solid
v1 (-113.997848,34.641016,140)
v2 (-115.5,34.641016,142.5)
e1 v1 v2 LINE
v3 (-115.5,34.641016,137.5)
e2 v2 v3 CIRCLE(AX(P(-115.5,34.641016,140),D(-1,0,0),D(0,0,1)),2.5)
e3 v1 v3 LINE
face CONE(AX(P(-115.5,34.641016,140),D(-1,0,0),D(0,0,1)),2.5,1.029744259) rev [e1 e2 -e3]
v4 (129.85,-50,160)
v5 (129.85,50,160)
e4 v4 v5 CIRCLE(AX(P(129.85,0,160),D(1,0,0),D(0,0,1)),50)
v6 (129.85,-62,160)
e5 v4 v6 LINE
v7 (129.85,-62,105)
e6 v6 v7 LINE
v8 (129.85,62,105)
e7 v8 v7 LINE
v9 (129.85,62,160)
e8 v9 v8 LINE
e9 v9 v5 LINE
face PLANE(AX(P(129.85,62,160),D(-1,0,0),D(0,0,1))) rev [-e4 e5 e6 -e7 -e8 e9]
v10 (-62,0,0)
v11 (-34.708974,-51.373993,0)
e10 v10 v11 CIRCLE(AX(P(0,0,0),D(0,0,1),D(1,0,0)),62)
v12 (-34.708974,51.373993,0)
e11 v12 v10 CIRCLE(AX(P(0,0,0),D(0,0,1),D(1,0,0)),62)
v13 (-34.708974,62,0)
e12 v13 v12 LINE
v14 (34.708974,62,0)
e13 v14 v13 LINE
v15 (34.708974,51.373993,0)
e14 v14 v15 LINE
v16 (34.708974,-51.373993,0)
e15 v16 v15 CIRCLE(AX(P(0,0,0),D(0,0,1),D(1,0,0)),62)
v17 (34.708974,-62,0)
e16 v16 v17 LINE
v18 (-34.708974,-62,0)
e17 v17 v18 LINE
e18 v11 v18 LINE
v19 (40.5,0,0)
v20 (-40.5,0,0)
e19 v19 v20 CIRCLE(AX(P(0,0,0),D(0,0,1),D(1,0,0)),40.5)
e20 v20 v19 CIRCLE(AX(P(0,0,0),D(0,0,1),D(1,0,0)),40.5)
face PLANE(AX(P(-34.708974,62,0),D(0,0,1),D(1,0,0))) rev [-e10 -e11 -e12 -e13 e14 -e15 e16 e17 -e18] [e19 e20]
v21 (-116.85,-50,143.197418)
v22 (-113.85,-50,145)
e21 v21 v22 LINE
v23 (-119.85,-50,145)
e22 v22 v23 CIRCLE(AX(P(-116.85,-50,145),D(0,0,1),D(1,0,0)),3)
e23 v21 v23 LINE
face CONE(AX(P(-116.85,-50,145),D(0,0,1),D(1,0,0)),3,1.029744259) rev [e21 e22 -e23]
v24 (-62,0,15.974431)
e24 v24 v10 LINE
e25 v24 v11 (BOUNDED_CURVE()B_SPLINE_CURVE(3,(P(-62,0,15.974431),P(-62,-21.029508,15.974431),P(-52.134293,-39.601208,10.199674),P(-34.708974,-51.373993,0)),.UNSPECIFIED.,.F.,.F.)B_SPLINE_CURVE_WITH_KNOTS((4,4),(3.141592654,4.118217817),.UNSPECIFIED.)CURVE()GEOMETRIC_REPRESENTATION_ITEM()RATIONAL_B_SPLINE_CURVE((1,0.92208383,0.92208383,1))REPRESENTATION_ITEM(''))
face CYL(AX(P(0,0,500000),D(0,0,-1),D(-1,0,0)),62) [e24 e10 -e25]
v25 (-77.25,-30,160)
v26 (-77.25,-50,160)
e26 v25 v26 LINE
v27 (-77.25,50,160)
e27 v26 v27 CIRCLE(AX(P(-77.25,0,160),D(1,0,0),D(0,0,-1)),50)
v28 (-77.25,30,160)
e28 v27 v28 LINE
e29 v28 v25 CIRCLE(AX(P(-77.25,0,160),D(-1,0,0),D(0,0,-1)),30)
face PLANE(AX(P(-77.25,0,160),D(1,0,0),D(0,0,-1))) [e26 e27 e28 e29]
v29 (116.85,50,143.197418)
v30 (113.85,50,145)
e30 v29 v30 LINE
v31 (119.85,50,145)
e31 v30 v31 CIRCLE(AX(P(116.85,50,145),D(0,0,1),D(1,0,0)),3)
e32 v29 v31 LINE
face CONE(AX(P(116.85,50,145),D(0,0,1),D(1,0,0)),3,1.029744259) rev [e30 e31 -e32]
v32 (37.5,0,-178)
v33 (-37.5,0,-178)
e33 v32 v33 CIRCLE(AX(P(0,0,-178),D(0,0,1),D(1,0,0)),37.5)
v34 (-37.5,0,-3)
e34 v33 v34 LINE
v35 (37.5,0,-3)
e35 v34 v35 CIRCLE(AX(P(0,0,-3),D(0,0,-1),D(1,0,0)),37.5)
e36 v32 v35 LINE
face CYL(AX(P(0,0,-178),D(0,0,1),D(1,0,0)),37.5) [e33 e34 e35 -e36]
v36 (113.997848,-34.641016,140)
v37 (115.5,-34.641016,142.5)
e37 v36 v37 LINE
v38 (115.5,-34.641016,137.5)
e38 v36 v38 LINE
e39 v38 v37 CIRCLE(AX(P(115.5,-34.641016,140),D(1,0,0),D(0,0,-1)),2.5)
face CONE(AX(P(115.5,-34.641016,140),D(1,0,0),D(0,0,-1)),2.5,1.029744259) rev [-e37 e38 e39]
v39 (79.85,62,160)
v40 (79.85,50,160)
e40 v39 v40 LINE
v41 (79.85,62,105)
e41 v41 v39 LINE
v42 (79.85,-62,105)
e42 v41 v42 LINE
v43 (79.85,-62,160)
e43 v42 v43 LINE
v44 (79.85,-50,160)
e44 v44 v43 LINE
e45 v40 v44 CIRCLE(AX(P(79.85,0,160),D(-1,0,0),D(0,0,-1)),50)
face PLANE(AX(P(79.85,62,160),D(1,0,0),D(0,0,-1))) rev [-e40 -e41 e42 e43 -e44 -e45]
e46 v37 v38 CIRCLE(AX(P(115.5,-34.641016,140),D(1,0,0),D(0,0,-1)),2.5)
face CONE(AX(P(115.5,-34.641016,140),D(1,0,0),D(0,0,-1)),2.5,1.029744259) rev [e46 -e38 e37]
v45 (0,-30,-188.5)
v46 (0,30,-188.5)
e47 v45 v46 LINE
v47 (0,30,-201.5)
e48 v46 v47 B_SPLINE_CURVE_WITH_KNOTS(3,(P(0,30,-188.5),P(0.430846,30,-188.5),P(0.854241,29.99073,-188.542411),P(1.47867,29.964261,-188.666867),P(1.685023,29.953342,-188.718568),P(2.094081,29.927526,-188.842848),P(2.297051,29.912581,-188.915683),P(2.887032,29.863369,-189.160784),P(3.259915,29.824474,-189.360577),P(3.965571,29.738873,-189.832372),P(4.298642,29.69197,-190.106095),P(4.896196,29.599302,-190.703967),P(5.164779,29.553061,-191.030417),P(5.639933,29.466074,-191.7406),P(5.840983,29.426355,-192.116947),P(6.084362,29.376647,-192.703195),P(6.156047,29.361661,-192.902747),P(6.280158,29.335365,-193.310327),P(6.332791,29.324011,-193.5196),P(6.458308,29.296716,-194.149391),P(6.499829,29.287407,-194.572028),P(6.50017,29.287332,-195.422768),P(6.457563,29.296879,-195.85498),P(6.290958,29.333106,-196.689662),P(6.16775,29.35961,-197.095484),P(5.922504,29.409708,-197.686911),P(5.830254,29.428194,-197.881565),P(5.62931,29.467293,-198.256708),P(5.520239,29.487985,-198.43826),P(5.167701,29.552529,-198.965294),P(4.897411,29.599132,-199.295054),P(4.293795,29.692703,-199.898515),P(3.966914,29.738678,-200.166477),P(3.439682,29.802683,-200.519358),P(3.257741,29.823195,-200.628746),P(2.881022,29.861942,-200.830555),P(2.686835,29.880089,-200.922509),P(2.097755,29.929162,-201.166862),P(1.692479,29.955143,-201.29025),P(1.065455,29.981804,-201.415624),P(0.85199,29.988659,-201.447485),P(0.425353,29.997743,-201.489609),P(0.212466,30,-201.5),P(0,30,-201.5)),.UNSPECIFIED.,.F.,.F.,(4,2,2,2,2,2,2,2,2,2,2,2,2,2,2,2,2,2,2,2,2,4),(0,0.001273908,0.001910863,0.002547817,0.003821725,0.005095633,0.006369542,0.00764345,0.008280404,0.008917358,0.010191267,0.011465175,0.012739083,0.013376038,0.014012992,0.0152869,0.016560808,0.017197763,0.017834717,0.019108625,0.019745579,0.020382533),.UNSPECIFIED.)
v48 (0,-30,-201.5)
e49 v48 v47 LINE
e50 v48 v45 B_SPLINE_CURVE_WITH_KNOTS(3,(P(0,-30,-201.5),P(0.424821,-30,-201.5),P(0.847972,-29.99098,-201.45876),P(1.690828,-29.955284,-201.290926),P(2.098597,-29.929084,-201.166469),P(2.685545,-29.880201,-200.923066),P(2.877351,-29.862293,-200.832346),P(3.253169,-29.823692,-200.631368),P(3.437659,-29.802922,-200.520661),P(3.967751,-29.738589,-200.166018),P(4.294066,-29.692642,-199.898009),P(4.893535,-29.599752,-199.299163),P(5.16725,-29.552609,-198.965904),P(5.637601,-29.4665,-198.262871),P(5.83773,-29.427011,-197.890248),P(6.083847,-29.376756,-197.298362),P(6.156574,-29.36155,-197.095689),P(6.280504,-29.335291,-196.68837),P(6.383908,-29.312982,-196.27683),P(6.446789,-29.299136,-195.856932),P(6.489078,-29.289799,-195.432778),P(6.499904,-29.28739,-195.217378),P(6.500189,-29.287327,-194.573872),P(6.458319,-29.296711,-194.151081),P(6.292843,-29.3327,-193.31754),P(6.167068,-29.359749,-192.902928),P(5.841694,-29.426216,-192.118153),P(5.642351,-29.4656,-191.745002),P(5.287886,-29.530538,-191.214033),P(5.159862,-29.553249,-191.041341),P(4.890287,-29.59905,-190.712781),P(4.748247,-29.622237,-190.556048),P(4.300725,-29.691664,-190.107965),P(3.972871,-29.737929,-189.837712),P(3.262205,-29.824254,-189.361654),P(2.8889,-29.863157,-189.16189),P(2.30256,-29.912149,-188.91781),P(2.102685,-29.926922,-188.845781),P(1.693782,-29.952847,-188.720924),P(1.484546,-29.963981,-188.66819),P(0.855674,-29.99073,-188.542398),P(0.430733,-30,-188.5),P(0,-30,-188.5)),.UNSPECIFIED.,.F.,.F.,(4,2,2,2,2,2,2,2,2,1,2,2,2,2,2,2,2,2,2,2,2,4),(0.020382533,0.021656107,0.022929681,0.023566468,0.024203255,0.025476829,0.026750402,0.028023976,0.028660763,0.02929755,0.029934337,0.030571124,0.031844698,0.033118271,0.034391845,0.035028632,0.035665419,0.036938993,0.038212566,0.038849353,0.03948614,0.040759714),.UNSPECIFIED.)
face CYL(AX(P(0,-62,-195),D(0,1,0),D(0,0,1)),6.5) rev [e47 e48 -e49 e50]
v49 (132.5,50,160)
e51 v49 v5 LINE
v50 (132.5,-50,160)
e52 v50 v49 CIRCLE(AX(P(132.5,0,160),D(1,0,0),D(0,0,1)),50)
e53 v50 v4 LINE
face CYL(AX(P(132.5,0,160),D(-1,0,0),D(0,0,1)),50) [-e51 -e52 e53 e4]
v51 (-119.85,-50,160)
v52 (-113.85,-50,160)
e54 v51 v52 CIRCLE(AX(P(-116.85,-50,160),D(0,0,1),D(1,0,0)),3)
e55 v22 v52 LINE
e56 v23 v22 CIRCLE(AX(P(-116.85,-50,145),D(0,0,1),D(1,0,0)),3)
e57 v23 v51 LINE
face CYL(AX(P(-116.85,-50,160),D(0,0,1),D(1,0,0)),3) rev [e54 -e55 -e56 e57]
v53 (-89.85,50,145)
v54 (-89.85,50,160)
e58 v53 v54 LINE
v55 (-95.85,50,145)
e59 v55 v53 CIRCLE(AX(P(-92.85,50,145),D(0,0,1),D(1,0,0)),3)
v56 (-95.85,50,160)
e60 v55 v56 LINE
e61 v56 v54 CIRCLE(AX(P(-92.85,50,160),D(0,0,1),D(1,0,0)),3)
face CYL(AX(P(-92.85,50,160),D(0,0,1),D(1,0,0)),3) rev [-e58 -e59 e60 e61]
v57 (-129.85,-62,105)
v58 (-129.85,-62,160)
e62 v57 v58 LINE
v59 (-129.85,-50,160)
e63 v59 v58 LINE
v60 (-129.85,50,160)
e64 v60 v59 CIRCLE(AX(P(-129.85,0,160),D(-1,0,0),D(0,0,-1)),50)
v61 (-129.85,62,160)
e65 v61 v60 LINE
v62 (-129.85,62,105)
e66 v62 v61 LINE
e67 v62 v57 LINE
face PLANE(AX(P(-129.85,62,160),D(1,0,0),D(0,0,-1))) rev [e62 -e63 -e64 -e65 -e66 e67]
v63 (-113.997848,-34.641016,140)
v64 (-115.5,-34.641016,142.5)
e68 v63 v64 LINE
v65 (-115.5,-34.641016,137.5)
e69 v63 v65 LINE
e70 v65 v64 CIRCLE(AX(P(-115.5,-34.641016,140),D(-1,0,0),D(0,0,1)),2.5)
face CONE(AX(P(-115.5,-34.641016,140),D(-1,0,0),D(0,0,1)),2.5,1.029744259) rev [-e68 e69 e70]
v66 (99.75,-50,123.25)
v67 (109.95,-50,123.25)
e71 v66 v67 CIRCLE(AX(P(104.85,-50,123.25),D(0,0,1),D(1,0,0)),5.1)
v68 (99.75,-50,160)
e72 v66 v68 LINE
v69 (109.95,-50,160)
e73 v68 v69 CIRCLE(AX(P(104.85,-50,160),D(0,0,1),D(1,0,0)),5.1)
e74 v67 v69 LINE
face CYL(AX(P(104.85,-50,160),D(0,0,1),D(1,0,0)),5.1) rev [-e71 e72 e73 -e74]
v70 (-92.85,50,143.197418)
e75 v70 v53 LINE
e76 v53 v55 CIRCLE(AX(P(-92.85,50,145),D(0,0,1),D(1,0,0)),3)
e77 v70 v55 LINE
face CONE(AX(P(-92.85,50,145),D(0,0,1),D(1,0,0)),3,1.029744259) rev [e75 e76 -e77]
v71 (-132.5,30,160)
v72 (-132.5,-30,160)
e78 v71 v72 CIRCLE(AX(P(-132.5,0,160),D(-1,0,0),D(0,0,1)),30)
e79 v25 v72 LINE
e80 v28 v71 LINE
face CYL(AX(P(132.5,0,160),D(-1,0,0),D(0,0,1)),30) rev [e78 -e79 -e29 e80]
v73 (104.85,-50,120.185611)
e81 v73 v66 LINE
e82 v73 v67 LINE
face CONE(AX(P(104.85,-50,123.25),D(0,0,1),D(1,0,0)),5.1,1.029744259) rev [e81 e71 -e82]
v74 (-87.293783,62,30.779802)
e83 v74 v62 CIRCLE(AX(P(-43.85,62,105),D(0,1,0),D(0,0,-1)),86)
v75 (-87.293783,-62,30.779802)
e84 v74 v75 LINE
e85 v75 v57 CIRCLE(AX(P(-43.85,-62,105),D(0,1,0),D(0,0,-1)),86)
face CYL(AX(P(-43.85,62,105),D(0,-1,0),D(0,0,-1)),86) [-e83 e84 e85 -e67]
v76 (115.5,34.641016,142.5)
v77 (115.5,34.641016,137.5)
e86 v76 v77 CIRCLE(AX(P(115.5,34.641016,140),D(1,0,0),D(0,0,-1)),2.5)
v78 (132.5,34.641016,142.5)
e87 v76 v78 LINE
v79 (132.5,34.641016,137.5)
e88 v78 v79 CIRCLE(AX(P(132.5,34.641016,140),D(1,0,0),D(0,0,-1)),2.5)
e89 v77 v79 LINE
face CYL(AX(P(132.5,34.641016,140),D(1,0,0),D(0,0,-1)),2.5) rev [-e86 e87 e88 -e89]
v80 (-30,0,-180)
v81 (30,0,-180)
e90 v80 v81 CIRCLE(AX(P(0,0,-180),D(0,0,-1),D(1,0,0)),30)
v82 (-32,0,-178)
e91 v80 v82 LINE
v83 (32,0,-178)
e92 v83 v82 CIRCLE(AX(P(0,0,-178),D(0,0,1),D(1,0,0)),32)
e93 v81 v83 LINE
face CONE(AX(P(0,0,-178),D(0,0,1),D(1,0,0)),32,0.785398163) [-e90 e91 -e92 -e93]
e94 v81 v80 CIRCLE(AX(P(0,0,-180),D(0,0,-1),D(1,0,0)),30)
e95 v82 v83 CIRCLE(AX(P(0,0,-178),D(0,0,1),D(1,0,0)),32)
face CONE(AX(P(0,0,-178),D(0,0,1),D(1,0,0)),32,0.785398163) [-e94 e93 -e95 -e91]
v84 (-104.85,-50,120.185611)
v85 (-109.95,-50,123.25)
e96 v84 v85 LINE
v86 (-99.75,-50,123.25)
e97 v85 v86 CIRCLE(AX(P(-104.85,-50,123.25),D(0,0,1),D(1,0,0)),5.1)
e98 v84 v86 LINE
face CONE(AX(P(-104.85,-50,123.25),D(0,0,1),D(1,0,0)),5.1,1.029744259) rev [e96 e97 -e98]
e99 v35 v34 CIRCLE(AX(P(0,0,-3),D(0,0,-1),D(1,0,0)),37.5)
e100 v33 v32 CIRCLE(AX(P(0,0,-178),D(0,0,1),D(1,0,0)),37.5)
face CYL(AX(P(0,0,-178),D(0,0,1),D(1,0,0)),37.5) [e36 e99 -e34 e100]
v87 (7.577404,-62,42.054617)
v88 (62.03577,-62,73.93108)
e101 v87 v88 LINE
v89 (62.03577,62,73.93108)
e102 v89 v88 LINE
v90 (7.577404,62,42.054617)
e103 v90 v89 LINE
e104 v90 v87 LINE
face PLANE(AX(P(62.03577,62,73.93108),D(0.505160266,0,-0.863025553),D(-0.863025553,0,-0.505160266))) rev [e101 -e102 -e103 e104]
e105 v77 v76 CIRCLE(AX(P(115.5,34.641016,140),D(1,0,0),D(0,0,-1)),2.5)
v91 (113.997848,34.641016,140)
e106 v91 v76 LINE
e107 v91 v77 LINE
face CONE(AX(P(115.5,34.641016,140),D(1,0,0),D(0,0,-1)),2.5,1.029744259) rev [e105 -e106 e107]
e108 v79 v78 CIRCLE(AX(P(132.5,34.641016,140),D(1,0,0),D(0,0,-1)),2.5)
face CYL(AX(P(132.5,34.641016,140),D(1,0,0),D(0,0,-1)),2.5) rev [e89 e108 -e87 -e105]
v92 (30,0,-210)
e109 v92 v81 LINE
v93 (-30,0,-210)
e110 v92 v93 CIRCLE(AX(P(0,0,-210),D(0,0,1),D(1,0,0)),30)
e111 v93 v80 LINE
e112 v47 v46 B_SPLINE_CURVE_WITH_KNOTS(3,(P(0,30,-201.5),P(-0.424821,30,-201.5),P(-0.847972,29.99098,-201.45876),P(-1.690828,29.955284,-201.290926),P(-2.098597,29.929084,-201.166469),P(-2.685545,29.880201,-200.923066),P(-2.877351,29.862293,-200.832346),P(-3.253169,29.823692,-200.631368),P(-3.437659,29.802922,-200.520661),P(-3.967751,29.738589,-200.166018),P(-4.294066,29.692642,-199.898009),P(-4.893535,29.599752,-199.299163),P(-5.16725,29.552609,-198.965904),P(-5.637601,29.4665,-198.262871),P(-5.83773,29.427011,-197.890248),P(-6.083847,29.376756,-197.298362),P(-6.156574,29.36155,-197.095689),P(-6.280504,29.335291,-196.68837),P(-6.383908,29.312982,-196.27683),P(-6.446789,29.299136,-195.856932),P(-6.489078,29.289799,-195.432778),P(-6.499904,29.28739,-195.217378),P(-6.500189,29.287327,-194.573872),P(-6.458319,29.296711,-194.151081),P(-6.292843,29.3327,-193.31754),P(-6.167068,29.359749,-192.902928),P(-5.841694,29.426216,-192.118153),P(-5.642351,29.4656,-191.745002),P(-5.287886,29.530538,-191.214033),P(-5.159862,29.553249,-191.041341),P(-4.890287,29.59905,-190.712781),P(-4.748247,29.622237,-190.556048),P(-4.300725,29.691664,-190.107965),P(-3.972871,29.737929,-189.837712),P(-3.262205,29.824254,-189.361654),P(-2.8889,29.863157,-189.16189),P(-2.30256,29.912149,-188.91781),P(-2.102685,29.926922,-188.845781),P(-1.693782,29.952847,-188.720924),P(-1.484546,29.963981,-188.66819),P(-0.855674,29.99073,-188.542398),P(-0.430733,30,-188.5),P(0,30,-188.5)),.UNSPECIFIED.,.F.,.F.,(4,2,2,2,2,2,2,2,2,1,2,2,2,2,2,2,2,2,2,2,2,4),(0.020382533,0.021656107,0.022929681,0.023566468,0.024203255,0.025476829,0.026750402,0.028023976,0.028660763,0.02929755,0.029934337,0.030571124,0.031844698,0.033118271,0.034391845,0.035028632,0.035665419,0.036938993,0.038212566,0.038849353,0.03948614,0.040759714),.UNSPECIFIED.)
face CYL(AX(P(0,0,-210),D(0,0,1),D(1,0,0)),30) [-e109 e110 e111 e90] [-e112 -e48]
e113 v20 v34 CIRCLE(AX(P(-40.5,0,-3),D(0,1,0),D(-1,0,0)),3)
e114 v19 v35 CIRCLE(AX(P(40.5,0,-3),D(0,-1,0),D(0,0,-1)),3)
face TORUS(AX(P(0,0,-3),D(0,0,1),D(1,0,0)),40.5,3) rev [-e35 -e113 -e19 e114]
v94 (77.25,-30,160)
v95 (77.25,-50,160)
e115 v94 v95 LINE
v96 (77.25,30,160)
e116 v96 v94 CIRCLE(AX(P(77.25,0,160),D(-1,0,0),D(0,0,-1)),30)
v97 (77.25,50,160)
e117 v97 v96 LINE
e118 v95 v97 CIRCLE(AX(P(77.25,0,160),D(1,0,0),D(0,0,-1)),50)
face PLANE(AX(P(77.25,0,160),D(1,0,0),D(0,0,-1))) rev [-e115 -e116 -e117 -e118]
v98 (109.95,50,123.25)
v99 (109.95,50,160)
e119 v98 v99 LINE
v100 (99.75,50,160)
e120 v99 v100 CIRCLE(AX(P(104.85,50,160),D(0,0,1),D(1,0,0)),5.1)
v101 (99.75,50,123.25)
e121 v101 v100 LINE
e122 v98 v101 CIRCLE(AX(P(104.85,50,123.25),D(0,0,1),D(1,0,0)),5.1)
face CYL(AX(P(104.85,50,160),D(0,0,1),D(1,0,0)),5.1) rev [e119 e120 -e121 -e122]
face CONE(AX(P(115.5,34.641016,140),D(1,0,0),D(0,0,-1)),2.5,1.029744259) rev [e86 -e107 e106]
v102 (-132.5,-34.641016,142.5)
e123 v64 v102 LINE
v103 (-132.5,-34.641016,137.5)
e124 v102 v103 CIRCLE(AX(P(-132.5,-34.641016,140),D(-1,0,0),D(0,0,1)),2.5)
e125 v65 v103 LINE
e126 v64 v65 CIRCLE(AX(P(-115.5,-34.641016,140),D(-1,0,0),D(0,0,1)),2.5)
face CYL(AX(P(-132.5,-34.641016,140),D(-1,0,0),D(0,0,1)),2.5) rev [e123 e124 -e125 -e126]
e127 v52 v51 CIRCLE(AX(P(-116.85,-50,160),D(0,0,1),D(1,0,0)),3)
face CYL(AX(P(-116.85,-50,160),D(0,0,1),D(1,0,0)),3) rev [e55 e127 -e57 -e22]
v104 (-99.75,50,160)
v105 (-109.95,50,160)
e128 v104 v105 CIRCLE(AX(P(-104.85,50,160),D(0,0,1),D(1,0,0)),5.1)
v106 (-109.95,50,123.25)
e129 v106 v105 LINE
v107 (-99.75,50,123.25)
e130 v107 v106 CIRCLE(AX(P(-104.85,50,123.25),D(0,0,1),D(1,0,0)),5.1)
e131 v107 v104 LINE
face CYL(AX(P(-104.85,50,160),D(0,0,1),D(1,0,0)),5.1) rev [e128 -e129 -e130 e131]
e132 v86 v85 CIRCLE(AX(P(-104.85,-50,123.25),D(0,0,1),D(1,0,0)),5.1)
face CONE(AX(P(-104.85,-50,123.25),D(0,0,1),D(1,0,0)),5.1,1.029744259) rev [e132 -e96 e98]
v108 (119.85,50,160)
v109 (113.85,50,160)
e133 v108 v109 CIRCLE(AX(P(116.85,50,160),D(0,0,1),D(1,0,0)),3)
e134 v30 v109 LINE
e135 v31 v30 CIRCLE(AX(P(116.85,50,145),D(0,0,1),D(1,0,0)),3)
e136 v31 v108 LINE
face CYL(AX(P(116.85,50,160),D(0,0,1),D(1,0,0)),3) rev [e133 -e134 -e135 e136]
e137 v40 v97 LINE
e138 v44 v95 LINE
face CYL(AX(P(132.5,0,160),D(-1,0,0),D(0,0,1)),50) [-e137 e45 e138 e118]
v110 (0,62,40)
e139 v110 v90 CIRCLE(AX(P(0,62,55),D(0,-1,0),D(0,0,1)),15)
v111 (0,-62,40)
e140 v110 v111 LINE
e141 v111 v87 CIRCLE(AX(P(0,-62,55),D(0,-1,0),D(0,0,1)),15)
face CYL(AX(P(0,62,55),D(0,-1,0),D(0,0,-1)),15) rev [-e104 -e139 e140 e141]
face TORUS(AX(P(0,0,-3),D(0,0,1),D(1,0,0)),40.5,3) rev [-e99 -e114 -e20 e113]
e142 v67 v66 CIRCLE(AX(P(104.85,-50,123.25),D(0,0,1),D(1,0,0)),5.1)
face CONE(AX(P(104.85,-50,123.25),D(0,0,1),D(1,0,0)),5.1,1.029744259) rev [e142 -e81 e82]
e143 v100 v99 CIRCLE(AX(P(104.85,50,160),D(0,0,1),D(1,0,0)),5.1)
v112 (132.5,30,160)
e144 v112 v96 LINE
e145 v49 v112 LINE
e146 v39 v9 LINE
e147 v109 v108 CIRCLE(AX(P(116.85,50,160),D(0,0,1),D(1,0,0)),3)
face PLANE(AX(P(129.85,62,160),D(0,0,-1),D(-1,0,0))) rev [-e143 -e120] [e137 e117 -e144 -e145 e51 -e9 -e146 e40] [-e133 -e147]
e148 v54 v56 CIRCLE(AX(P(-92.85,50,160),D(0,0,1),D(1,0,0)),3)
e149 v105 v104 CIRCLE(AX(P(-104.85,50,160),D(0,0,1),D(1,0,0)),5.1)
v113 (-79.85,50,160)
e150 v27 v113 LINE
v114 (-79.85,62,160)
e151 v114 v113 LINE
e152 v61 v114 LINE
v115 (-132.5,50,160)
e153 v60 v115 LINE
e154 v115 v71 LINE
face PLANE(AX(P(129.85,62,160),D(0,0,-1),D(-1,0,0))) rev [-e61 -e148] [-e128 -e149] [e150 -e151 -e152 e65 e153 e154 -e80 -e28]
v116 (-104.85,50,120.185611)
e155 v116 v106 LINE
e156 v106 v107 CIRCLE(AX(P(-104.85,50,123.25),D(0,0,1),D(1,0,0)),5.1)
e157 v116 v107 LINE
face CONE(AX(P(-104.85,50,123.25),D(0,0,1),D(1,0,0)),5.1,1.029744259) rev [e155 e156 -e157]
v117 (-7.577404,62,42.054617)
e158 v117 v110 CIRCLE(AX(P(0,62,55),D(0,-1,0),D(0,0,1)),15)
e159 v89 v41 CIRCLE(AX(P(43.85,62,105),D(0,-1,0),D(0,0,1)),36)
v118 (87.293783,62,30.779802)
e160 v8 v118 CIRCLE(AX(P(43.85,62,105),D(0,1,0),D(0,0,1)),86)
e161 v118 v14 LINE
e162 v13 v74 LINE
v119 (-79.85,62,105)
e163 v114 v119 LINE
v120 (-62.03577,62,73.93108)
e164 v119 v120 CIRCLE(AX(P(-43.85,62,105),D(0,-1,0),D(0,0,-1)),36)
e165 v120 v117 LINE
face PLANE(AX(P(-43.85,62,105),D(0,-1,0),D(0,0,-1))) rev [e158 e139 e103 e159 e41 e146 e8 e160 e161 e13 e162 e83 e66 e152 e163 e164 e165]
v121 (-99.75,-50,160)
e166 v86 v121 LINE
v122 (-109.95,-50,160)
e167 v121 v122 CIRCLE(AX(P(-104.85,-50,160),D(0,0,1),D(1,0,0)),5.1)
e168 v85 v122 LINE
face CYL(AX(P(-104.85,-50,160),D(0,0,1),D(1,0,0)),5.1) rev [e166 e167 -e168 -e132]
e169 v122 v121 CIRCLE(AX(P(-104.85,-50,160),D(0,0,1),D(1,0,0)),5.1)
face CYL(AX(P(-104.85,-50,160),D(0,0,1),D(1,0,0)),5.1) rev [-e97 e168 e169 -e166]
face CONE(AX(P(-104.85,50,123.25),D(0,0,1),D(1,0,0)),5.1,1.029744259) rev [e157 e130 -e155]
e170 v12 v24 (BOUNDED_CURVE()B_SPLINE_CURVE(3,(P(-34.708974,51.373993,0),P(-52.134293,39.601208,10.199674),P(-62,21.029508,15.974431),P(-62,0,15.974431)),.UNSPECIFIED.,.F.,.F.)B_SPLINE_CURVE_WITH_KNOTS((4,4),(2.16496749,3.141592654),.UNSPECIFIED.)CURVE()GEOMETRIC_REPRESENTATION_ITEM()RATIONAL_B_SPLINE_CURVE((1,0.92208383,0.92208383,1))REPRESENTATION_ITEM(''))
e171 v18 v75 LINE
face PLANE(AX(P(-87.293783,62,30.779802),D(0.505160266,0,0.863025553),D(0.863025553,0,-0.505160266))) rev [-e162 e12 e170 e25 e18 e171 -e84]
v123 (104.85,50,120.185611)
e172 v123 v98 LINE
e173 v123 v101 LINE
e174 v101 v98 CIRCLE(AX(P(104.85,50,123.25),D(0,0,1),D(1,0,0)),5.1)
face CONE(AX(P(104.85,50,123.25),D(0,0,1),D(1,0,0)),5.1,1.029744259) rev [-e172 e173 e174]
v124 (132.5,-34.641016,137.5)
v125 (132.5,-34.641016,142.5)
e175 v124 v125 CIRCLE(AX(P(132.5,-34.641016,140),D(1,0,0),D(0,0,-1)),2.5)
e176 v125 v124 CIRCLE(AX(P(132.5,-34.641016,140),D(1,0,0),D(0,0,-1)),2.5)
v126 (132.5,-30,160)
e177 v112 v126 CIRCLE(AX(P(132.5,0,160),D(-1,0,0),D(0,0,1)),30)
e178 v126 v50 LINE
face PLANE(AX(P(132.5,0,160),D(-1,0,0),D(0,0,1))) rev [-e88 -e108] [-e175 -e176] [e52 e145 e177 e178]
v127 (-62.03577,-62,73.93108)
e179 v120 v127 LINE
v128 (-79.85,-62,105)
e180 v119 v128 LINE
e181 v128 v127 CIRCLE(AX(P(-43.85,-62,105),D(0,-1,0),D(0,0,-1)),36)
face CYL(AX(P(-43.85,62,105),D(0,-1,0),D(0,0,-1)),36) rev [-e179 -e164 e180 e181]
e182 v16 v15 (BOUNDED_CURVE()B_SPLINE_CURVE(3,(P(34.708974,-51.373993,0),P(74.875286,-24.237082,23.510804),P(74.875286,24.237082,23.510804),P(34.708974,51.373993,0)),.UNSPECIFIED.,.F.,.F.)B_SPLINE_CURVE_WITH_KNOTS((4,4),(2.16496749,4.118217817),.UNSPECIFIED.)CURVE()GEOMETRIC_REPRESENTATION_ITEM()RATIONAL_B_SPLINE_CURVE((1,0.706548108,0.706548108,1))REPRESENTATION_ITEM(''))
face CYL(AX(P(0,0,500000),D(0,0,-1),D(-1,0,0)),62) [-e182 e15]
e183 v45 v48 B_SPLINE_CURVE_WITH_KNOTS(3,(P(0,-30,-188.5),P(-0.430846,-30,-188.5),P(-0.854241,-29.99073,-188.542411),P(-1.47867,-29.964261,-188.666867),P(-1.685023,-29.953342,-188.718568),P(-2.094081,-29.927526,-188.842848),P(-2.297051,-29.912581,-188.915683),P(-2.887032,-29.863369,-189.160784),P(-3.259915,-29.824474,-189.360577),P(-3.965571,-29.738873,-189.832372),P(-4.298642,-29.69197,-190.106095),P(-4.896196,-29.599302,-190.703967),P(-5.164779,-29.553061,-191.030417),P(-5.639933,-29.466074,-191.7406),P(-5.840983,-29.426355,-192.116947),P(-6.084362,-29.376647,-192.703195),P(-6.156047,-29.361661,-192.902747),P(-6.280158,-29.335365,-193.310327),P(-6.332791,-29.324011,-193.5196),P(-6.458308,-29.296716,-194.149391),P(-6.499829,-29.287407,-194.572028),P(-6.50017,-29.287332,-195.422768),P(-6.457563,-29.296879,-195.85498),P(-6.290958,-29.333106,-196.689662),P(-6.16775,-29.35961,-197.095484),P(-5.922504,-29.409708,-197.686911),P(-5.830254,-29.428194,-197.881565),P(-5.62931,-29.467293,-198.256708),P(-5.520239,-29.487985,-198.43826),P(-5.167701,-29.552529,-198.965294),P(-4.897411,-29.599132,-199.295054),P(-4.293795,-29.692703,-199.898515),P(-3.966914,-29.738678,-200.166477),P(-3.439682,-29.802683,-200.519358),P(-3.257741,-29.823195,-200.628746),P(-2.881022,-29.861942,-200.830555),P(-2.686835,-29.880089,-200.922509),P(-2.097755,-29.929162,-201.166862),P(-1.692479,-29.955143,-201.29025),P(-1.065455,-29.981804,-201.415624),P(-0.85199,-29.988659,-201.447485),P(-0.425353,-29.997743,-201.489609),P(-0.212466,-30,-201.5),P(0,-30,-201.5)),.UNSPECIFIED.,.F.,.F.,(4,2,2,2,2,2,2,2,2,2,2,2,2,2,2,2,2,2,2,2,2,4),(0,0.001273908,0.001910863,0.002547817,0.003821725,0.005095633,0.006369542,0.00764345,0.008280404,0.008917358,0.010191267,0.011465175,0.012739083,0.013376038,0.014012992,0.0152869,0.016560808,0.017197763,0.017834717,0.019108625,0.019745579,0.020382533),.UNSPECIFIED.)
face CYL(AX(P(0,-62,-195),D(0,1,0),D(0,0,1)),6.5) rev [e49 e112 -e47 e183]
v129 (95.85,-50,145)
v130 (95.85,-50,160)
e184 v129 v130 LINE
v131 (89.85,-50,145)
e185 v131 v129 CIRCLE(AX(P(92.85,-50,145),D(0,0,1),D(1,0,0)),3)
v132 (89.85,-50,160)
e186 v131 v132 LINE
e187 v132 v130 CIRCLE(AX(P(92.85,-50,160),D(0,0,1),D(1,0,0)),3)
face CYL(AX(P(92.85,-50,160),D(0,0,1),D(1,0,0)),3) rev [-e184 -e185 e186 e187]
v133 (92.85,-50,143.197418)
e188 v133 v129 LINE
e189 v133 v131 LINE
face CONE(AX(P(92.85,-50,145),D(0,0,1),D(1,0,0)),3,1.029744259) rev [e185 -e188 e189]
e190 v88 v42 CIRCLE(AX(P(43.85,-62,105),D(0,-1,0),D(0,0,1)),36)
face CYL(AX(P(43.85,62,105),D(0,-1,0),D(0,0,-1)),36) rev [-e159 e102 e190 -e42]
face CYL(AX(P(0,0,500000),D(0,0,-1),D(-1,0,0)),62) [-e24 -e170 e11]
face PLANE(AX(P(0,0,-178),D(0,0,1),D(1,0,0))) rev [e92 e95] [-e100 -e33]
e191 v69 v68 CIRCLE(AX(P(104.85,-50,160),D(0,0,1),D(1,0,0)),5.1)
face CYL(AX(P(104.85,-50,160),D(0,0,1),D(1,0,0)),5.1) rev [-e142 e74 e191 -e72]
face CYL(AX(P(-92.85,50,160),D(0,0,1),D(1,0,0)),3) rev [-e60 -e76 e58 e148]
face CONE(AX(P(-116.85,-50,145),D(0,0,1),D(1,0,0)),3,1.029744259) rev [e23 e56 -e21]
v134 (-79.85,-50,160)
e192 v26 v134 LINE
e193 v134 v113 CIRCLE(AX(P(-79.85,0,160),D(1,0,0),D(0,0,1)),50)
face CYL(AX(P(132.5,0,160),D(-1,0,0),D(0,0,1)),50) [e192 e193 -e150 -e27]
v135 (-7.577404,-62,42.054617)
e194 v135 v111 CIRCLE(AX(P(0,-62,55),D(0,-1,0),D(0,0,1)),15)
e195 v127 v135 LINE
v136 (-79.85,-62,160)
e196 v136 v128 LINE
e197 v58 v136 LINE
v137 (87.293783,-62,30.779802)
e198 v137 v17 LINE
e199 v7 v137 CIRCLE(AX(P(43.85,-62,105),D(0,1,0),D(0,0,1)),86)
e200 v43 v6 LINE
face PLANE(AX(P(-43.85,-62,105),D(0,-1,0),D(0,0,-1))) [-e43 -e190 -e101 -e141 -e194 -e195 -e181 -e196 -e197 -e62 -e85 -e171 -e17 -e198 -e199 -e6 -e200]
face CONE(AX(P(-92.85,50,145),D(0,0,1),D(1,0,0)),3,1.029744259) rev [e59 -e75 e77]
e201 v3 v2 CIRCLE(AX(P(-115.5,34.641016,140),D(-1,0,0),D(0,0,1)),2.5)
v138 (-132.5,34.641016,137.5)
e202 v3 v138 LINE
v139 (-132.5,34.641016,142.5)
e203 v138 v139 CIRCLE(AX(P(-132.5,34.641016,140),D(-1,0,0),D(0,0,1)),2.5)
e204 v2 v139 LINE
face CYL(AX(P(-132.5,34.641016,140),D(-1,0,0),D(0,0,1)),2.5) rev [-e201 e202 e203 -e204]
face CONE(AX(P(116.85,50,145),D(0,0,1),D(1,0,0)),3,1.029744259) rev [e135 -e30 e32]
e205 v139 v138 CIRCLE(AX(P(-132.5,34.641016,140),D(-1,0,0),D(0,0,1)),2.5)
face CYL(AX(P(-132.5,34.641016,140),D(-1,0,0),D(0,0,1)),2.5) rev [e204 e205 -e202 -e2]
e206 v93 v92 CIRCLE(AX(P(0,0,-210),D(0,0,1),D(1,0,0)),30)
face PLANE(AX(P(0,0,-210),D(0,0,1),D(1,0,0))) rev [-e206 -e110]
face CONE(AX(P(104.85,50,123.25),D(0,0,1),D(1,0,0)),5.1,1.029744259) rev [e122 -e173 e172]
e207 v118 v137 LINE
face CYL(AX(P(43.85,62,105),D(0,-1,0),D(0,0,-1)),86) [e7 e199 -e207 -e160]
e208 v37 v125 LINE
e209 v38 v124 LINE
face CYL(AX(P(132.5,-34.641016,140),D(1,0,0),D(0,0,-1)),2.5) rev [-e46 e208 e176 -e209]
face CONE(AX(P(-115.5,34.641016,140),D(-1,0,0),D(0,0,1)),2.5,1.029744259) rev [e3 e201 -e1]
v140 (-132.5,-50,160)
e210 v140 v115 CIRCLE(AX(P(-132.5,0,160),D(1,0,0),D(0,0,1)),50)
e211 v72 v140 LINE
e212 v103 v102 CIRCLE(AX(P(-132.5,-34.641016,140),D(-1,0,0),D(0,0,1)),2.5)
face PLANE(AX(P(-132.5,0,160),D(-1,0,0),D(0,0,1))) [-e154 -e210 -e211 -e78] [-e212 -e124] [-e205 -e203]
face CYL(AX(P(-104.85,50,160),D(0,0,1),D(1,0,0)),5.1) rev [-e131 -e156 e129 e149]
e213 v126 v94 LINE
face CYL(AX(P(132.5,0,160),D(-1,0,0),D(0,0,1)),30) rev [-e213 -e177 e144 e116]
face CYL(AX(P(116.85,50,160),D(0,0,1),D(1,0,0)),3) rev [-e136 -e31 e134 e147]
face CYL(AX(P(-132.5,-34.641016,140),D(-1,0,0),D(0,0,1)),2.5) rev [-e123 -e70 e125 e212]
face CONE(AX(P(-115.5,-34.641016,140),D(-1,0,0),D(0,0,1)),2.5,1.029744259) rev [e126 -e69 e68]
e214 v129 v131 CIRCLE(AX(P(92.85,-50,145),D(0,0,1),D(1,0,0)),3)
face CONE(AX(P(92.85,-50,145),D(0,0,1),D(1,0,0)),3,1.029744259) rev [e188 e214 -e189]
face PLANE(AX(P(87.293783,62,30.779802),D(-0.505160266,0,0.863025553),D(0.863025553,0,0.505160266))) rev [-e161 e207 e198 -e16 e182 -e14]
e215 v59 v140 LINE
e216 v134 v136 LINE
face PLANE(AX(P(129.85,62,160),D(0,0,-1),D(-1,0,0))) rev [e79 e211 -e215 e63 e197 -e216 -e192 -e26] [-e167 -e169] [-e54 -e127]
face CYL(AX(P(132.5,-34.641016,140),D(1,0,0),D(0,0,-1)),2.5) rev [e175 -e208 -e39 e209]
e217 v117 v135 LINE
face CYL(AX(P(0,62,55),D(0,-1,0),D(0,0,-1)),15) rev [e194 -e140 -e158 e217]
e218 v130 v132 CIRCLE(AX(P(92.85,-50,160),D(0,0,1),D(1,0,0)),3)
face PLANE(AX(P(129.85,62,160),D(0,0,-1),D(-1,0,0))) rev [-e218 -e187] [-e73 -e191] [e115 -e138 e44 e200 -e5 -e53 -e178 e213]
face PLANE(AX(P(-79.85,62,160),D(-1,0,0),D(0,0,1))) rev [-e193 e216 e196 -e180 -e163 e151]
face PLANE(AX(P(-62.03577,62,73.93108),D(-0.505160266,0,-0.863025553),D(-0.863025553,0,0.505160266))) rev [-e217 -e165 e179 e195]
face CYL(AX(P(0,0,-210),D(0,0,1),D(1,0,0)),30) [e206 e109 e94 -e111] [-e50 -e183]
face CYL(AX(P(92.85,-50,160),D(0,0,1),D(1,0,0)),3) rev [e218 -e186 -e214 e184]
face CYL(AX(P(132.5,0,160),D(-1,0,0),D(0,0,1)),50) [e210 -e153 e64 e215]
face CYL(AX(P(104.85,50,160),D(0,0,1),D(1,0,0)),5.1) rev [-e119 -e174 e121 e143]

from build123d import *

# Parameters (mm, degrees)
BOSS_EXTRUDE1_DEPTH         = 62
SKETCH2_R                   = 62
BOSS_EXTRUDE2_DEPTH         = 15.974431
SKETCH3_R                   = 37.5
BOSS_EXTRUDE3_DEPTH         = 178
SKETCH4_R                   = 30
BOSS_EXTRUDE4_DEPTH         = 210
CUT_EXTRUDE1_DEPTH          = 255.568306158
CUT_EXTRUDE1_DEPTH_BACK     = 255.568306158
SKETCH5_R                   = 6.5
BOSS_EXTRUDE5_DEPTH         = 132.5
CUT_EXTRUDE2_DEPTH          = 77.25
CUT_EXTRUDE3_DEPTH          = 256.930166338
CUT_EXTRUDE3_DEPTH_BACK     = 256.930166338
M6_TAPPED_HOLE1_AT_2_COUNT  = 2
M6_TAPPED_HOLE1_AT_2_PITCH  = 69.282032303
M12_TAPPED_HOLE1_D          = 10.2
M12_TAPPED_HOLE1_DEPTH      = 36.75
M12_TAPPED_HOLE1_TIP        = 3.064389157
F_6MM_BLIND_PIN_HOLE1_D     = 6
F_6MM_BLIND_PIN_HOLE1_DEPTH = 15
F_6MM_BLIND_PIN_HOLE1_TIP   = 1.802581857
CHAMFER1_SIZE               = 2
FILLET1_R                   = 3


with BuildPart() as part:
    # Sketch1 → Boss-Extrude1 (new, symmetric)
    with BuildSketch(Plane(origin=(0, 0, 0), x_dir=(1, 0, 0), z_dir=(0, 1, 0))):
        with BuildLine():
            Line((-129.85, -160), (-79.85, -160))
            Line((-79.85, -160), (-79.85, -105))
            ThreePointArc((-79.85, -105), (-75.080495551, -87.093125688), (-62.035769577, -73.931080081))
            Line((-62.035769577, -73.931080081), (-7.57740399, -42.054616701))
            ThreePointArc((-7.57740399, -42.054616701), (0, -40), (7.57740399, -42.054616701))
            Line((7.57740399, -42.054616701), (62.035769577, -73.931080081))
            ThreePointArc((62.035769577, -73.931080081), (75.080495551, -87.093125688), (79.85, -105))
            Line((79.85, -105), (79.85, -160))
            Line((79.85, -160), (129.85, -160))
            Line((129.85, -160), (129.85, -105))
            ThreePointArc((129.85, -105), (118.456183817, -62.222466922), (87.293782877, -30.779802417))
            Line((87.293782877, -30.779802417), (34.708974059, 0))
            Line((34.708974059, 0), (-34.708974059, 0))
            Line((-34.708974059, 0), (-87.293782877, -30.779802417))
            ThreePointArc((-87.293782877, -30.779802417), (-118.456183817, -62.222466922), (-129.85, -105))
            Line((-129.85, -105), (-129.85, -160))
        make_face()
    extrude(amount=BOSS_EXTRUDE1_DEPTH, both=True)

    # Sketch2 → Boss-Extrude2 (add)
    with BuildSketch(Plane.XY):
        Circle(SKETCH2_R)
    extrude(amount=BOSS_EXTRUDE2_DEPTH)

    # Sketch3 → Boss-Extrude3 (add)
    with BuildSketch(Plane.XY):
        Circle(SKETCH3_R)
    extrude(amount=-BOSS_EXTRUDE3_DEPTH)

    # Sketch4 → Boss-Extrude4 (add)
    with BuildSketch(Plane.XY):
        Circle(SKETCH4_R)
    extrude(amount=-BOSS_EXTRUDE4_DEPTH)

    # Sketch5 → Cut-Extrude1 (cut, two sides: drawn at the far end of the back side and taken through both)
    with BuildSketch(Plane(origin=(0, 0, 0), x_dir=(1, 0, 0), z_dir=(0, 1, 0)).offset(-CUT_EXTRUDE1_DEPTH_BACK)):
        with Locations(Location((0, 195, 0), (0, 0, 270))):
            Circle(SKETCH5_R)
    extrude(amount=CUT_EXTRUDE1_DEPTH + CUT_EXTRUDE1_DEPTH_BACK, mode=Mode.SUBTRACT)

    # Sketch6 → Boss-Extrude5 (add, symmetric)
    with BuildSketch(Plane(origin=(0, 0, 0), x_dir=(0, 0, -1), z_dir=(1, 0, 0))):
        with BuildLine():
            Line((-160, 50), (-160, 30))
            ThreePointArc((-160, 30), (-130, 0), (-160, -30))
            Line((-160, -30), (-160, -50))
            ThreePointArc((-160, -50), (-110, 0), (-160, 50))
        make_face()
    extrude(amount=BOSS_EXTRUDE5_DEPTH, both=True)

    # Sketch7 → Cut-Extrude2 (cut, symmetric)
    with BuildSketch(Plane(origin=(0, 0, 0), x_dir=(0, 0, -1), z_dir=(1, 0, 0))):
        with BuildLine():
            Line((-160, 28), (-160, 52))
            ThreePointArc((-160, 52), (-108, 0), (-160, -52))
            Line((-160, -52), (-160, -28))
            ThreePointArc((-160, -28), (-132, 0), (-160, 28))
        make_face()
    extrude(amount=CUT_EXTRUDE2_DEPTH, both=True, mode=Mode.SUBTRACT)

    # Sketch15 → Cut-Extrude3 (cut, two sides: drawn at the far end of the back side and taken through both)
    with BuildSketch(Plane(origin=(0, 0, 0), x_dir=(0, 0, -1), z_dir=(1, 0, 0)).offset(-CUT_EXTRUDE3_DEPTH_BACK)):
        with BuildLine():
            Line((-160, 30), (-160, -30))
            ThreePointArc((-160, -30), (-130, 0), (-160, 30))
        make_face()
    extrude(amount=CUT_EXTRUDE3_DEPTH + CUT_EXTRUDE3_DEPTH_BACK, mode=Mode.SUBTRACT)

    # Sketch8 → M6 Tapped Hole1 (revolve, cut)
    with BuildSketch(Plane(origin=(132.5, 34.641016151, 140), x_dir=(0, 0, -1), z_dir=(0, 1, 0))):
        Polygon((0, 0), (0, 18.502151548), (2.5, 17), (2.5, 0), align=None)
    m6_tapped_hole1 = revolve(axis=Axis((138.85, 34.641016151, 140), (-1, 0, 0)), mode=Mode.SUBTRACT)

    # M6 Tapped Hole1 at 2: M6 Tapped Hole1 ×2
    with Locations(*[(0, -i * M6_TAPPED_HOLE1_AT_2_PITCH, 0) for i in range(1, M6_TAPPED_HOLE1_AT_2_COUNT)]):
        add(m6_tapped_hole1, mode=Mode.SUBTRACT)

    # Mirror1: M6 Tapped Hole1 across plane
    add(m6_tapped_hole1.mirror(Plane(origin=(0, 0, 0), x_dir=(0, 0, 1), z_dir=(1, 0, 0))), mode=Mode.SUBTRACT)

    # Mirror1 copy 1 sketch → Mirror1 copy 1 (revolve, cut)
    with BuildSketch(Plane(origin=(-132.5, -34.641016151, 140), x_dir=(0, 0, -1), z_dir=(0, 1, 0))):
        Polygon((0, 0), (0, -18.502151548), (2.5, -17), (2.5, 0), align=None)
    revolve(axis=Axis((-138.85, -34.641016151, 140), (-1, 0, 0)), mode=Mode.SUBTRACT)

    # M12 Tapped Hole1
    with Locations(Plane.XY.offset(160)):
        with Locations((104.85, 50), (104.85, -50), (-104.85, 50), (-104.85, -50)):
            Hole(M12_TAPPED_HOLE1_D / 2, depth=M12_TAPPED_HOLE1_DEPTH)
            with Locations((0, 0, -(M12_TAPPED_HOLE1_DEPTH + M12_TAPPED_HOLE1_TIP / 2))):  # 118° drill point
                Cone(0, M12_TAPPED_HOLE1_D / 2, M12_TAPPED_HOLE1_TIP, mode=Mode.SUBTRACT)

    # 6mm blind pin hole1
    with Locations(Plane.XY.offset(160)):
        with Locations((116.85, 50), (92.85, -50), (-92.85, 50), (-116.85, -50)):
            Hole(F_6MM_BLIND_PIN_HOLE1_D / 2, depth=F_6MM_BLIND_PIN_HOLE1_DEPTH)
            with Locations((0, 0, -(F_6MM_BLIND_PIN_HOLE1_DEPTH + F_6MM_BLIND_PIN_HOLE1_TIP / 2))):  # 118° drill point
                Cone(0, F_6MM_BLIND_PIN_HOLE1_D / 2, F_6MM_BLIND_PIN_HOLE1_TIP, mode=Mode.SUBTRACT)

    # Chamfer1
    chamfer1_edges = [part.edges().sort_by_distance(p)[0] for p in [
        (-30, 0, -178),
    ]]
    chamfer(chamfer1_edges, length=CHAMFER1_SIZE)

    # Fillet1
    fillet1_edges = [part.edges().sort_by_distance(p)[0] for p in [
        (-37.5, 0, 0),
    ]]
    fillet(fillet1_edges, radius=FILLET1_R)


solid = part.part
